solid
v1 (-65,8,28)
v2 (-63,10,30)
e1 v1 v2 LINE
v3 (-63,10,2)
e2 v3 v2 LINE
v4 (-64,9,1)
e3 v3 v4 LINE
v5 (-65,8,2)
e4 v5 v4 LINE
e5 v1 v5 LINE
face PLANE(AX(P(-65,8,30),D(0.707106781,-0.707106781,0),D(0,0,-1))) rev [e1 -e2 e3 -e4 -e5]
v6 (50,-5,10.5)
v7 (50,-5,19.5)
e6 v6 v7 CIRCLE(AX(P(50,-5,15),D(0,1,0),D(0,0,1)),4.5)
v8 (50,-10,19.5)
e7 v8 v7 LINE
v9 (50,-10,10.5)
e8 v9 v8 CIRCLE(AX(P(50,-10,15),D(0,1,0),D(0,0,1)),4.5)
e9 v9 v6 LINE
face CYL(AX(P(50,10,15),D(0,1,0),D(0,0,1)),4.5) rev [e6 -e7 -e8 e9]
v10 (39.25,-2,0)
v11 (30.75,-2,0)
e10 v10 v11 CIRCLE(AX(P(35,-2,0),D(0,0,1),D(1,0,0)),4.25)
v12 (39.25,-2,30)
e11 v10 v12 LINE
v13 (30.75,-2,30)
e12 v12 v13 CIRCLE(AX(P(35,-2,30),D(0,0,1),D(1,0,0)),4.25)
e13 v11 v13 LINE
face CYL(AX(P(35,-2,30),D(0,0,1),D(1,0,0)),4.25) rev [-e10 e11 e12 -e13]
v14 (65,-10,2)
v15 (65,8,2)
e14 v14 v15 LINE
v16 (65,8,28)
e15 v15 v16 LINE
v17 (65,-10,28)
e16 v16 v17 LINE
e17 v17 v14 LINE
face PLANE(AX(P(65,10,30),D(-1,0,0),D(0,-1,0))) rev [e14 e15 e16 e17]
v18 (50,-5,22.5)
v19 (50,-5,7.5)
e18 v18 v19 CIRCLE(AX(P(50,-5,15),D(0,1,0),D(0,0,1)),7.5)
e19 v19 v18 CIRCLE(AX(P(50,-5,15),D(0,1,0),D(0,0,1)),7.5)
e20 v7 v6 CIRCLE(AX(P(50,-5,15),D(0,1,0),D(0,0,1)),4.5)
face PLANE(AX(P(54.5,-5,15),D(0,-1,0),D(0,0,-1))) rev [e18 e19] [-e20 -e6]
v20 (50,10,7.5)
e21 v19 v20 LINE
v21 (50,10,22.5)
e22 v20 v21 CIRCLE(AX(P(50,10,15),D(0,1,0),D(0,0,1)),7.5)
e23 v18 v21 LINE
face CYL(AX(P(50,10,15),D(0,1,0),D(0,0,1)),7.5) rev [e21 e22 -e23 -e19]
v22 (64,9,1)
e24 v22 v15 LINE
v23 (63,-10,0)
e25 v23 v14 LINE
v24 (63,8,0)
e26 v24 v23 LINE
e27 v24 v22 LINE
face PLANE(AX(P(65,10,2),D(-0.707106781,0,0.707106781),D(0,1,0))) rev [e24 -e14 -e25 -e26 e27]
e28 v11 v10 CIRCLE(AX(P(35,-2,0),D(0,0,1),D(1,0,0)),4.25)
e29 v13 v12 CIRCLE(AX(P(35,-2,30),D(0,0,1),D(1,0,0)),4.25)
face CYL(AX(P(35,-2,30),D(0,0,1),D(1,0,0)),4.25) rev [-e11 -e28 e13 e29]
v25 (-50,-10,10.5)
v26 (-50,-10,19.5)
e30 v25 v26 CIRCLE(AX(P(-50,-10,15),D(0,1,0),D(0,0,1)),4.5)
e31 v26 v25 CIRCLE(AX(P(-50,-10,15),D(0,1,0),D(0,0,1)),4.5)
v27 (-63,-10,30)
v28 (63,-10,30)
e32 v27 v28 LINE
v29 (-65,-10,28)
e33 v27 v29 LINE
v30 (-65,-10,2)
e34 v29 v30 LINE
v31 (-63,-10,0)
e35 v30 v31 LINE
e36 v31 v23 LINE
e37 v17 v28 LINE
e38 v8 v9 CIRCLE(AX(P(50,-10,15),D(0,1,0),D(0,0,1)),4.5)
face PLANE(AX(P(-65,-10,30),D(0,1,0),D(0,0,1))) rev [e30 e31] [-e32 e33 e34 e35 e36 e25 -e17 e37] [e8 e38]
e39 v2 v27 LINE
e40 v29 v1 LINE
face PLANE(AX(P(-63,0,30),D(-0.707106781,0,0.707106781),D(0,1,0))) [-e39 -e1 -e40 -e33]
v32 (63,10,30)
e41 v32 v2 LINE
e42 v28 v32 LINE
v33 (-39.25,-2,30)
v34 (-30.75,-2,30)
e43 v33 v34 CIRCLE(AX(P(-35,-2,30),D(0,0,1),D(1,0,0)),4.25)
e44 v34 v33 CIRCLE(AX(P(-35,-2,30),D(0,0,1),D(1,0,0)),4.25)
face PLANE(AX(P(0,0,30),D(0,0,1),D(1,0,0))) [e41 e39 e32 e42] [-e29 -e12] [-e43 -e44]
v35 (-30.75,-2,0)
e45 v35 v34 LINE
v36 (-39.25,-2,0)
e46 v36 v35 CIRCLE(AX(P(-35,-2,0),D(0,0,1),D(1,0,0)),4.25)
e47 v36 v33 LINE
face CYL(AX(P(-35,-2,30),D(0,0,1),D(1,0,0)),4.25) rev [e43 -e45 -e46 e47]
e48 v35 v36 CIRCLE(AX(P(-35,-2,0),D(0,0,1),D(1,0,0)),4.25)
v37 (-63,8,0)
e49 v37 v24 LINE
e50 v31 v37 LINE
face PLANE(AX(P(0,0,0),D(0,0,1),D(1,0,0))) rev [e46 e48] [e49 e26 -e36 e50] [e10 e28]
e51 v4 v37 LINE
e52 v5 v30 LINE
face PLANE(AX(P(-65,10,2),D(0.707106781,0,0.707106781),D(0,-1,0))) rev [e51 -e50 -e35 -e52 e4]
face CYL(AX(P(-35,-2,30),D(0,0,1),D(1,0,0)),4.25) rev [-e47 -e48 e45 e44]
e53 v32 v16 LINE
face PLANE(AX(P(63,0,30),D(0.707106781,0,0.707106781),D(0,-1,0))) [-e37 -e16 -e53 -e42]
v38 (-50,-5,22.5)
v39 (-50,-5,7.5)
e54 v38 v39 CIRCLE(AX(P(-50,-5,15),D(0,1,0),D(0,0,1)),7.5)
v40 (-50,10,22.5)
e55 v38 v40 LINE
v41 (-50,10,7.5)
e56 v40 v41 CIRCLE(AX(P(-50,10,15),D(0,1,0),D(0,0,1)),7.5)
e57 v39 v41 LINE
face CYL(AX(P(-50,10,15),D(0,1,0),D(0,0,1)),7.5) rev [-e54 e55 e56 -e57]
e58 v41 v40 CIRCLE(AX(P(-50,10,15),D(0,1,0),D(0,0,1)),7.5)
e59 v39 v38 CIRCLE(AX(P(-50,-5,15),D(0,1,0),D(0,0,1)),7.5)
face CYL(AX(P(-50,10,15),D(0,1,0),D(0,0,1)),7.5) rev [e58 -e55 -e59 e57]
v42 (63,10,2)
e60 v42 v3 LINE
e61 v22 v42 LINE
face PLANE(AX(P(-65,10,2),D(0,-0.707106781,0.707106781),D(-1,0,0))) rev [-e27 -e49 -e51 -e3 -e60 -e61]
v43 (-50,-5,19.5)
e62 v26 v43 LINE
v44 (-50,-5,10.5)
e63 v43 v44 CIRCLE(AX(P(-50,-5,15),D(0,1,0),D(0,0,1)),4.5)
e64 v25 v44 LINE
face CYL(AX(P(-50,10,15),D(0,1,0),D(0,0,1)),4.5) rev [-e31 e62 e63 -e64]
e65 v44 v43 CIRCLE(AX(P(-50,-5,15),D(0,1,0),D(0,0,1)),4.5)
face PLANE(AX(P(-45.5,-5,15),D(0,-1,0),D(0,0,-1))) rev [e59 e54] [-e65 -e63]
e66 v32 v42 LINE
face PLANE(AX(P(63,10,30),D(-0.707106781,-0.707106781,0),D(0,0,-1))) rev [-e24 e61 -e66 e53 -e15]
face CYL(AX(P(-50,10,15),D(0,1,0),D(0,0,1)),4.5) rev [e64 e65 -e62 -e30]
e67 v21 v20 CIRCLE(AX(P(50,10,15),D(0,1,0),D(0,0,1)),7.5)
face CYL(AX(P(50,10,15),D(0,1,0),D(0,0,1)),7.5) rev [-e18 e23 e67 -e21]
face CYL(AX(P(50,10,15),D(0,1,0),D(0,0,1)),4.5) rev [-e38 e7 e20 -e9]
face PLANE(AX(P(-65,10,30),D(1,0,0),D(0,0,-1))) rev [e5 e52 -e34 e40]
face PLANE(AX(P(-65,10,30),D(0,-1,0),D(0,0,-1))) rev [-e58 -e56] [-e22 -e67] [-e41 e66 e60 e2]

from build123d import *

# Parameters (mm, degrees)
SKETCH_1_W                = 130
SKETCH_1_H                = 20
EXTRUDE_1_DEPTH           = 30
HOLE_WIZARD_1_D           = 9
HOLE_WIZARD_1_CBORE_D     = 15
HOLE_WIZARD_1_CBORE_DEPTH = 15
HOLE_WIZARD_M10_1_D       = 8.5
CHAMFER_1_SIZE            = 2
CHAMFER_2_SIZE            = 2


with BuildPart() as part:
    # 草图1 → 凸台-拉伸1 (new body)
    with BuildSketch(Plane.XY):
        Rectangle(SKETCH_1_W, SKETCH_1_H)
    extrude(amount=EXTRUDE_1_DEPTH)

    # 打孔尺寸(%根据)内六角圆柱头螺钉的类型1 (through all)
    with Locations(Plane(origin=(0, 10, 0), x_dir=(1, 0, 0), z_dir=(0, 1, 0))):
        with Locations((-50, -15), (50, -15)):
            CounterBoreHole(HOLE_WIZARD_1_D / 2, HOLE_WIZARD_1_CBORE_D / 2, HOLE_WIZARD_1_CBORE_DEPTH)

    # M10 螺纹孔1 (through all)
    with Locations(Plane.XY.offset(30)):
        with Locations((-35, -2), (35, -2)):
            Hole(HOLE_WIZARD_M10_1_D / 2)

    # 倒角1
    chamfer_1_edges = [part.edges().sort_by_distance(p)[0] for p in [
        (-65, 0, 30),
        (65, 0, 30),
        (-65, 0, 0),
        (65, 0, 0),
        (-65, 10, 15),
        (65, 10, 15),
    ]]
    chamfer(chamfer_1_edges, length=CHAMFER_1_SIZE)

    # 倒角2
    chamfer_2_edges = [part.edges().sort_by_distance(p)[0] for p in [
        (0, 10, 0),
    ]]
    chamfer(chamfer_2_edges, length=CHAMFER_2_SIZE)


solid = part.part
